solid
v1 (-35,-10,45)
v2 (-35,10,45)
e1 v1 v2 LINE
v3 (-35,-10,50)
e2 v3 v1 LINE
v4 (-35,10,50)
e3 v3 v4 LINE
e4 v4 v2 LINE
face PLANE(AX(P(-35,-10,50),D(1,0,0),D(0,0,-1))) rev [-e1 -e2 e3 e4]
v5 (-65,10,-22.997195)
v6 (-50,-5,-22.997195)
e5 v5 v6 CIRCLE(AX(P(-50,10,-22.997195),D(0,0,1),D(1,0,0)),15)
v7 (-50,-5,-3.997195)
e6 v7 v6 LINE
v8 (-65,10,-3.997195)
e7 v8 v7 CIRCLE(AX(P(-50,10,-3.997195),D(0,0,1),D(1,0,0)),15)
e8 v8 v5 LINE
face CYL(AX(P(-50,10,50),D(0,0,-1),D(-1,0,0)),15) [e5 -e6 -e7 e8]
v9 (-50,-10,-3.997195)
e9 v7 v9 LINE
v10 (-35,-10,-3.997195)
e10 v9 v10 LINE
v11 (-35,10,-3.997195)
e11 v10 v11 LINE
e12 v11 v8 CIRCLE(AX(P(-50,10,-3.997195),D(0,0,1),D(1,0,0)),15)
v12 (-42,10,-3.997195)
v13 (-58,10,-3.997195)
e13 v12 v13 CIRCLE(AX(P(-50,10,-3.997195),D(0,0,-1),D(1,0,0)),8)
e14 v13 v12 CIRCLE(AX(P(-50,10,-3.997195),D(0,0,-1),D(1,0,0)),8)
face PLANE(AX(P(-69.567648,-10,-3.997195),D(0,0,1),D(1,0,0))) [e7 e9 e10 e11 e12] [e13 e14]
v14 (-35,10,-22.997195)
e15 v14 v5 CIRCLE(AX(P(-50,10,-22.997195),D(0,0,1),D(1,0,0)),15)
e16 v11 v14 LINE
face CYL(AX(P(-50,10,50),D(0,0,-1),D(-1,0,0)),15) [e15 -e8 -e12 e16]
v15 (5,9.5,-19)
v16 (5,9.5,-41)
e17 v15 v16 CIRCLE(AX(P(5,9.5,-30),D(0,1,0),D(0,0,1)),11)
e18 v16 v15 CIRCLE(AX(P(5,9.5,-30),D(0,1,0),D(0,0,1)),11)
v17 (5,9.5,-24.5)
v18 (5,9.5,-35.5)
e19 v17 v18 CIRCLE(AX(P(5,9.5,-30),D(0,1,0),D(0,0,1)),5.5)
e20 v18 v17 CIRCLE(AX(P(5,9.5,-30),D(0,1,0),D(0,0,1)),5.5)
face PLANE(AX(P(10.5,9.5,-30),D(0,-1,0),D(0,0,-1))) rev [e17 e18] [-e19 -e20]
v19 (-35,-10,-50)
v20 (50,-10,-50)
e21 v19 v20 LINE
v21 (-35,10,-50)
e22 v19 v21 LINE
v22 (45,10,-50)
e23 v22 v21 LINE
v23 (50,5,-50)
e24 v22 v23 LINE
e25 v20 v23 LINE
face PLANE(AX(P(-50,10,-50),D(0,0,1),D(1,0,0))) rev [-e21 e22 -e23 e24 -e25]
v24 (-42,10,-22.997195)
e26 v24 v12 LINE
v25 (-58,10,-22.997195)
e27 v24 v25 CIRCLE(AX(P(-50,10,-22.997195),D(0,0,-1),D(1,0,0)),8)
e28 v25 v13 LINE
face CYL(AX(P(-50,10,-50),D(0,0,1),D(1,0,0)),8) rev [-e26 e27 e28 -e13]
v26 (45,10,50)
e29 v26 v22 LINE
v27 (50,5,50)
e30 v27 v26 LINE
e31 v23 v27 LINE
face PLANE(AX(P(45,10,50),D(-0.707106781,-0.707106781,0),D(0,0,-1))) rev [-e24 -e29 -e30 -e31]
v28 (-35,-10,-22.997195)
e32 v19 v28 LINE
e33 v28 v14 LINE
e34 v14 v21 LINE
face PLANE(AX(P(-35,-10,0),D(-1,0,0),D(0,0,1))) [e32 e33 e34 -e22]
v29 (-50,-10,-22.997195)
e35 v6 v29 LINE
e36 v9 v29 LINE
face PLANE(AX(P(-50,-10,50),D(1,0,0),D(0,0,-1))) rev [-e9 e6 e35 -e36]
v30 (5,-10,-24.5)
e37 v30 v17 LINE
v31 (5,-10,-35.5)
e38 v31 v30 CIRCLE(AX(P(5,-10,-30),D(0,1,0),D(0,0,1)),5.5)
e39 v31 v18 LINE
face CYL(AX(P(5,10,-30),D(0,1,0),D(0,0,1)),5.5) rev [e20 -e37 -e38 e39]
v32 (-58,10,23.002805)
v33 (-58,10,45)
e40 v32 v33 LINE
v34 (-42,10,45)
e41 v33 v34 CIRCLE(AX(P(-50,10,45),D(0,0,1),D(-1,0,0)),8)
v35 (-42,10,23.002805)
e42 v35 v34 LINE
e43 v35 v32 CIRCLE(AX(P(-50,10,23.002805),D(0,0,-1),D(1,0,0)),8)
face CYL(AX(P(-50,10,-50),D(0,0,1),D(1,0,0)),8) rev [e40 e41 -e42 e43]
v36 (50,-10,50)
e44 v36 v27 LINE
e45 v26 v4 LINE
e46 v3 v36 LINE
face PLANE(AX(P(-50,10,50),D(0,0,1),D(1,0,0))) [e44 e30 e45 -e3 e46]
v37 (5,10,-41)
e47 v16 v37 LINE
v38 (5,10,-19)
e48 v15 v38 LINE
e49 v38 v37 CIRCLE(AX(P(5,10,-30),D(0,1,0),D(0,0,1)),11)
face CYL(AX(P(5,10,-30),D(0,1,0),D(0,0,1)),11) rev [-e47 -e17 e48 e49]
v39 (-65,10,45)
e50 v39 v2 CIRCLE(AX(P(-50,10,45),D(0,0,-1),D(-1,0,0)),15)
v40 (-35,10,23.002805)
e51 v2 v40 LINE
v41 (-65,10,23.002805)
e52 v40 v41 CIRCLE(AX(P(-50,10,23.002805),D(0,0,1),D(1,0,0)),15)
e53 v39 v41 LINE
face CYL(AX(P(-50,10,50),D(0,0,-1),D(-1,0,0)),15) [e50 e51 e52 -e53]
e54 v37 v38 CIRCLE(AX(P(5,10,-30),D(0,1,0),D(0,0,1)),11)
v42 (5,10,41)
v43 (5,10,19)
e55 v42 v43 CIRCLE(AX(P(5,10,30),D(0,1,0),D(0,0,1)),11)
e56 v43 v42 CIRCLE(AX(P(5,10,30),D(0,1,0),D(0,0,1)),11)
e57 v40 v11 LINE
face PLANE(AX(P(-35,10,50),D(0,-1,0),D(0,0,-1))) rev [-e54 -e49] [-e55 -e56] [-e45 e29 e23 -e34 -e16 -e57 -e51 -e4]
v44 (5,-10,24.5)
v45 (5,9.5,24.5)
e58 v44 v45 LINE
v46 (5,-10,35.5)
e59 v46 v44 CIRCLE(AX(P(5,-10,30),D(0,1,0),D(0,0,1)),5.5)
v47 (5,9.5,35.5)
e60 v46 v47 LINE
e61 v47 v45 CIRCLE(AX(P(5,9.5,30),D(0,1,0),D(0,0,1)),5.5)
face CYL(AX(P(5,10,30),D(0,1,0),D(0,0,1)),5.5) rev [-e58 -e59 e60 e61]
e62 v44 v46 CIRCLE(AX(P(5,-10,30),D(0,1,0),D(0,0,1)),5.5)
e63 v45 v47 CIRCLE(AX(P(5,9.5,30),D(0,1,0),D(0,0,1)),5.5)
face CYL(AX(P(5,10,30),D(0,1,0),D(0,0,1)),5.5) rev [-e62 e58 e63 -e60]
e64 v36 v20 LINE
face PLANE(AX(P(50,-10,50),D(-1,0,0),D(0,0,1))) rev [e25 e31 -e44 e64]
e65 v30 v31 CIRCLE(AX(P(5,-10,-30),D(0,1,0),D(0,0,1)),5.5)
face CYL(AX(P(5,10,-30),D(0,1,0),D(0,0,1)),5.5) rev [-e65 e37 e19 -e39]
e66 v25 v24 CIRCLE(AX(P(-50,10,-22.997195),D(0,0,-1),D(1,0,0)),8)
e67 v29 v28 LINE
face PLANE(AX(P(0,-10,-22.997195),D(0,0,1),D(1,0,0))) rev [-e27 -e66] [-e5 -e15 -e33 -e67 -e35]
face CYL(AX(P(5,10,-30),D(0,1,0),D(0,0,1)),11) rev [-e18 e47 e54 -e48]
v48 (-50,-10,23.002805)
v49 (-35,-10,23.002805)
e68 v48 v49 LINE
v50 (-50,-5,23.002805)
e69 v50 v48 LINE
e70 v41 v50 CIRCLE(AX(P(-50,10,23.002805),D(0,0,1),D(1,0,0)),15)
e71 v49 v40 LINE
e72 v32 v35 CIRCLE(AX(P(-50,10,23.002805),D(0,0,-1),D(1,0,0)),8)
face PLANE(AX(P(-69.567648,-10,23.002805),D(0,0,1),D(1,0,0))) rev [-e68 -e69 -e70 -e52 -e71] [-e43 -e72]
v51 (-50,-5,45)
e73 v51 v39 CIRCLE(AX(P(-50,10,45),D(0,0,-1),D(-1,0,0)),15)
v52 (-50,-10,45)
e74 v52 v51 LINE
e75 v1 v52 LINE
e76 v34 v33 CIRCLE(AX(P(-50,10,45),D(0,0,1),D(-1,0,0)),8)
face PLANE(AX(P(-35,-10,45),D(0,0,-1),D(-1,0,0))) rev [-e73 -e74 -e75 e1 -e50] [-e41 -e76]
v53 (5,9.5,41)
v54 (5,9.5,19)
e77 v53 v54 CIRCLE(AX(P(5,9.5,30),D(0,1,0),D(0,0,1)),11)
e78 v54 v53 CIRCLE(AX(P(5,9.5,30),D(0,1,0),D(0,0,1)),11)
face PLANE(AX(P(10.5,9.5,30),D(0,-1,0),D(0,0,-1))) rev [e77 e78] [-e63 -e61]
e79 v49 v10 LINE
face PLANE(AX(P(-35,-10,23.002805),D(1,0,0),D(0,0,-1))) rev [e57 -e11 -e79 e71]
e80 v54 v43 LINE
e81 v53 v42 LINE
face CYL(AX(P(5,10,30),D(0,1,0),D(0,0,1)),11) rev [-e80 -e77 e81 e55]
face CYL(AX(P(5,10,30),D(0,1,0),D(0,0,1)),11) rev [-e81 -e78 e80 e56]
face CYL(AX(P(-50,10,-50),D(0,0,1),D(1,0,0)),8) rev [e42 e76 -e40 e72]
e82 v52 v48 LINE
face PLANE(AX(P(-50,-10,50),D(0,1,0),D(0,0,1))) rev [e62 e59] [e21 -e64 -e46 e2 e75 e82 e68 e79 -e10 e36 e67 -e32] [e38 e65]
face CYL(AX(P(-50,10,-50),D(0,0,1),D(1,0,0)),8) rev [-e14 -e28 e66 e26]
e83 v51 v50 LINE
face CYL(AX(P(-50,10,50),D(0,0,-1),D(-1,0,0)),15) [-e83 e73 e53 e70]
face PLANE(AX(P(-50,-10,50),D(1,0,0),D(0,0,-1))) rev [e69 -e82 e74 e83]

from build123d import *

# Parameters (mm, degrees)
EXTRUDE_2_DEPTH               = 50
CUT_EXTRUDE_1_DEPTH           = 122.86057607
CUT_EXTRUDE_1_DEPTH_BACK      = 122.86057607
SKETCH_2_R                    = 8
CUT_EXTRUDE_8_DEPTH           = 85.409715081
CUT_EXTRUDE_8_DEPTH_BACK      = 85.409715081
SKETCH_3_W                    = 34.567648094
SKETCH_3_H                    = 27
SKETCH_3_W_2                  = 34.56764798
SKETCH_3_H_2                  = 5
CHAMFER_1_SIZE                = 5
HOLE_WIZARD_M10_1_D           = 11
HOLE_WIZARD_M10_1_CBORE_D     = 22
HOLE_WIZARD_M10_1_CBORE_DEPTH = 0.5


with BuildPart() as part:
    # 草图1 → 凸台-拉伸2 (new, symmetric)
    with BuildSketch(Plane.XY):
        with BuildLine():
            Line((-50, -10), (50, -10))
            Line((50, -10), (50, 10))
            Line((50, 10), (-35, 10))
            ThreePointArc((-35, 10), (-60.606601718, 20.606601718), (-50, -5))
            Line((-50, -5), (-50, -10))
        make_face()
    extrude(amount=EXTRUDE_2_DEPTH, both=True)

    # 草图2 → 切除-拉伸1 (cut, two sides: drawn at the far end of the back side and taken through both)
    with BuildSketch(Plane.XY.offset(50).offset(-CUT_EXTRUDE_1_DEPTH_BACK)):
        with Locations((-50, 10)):
            Circle(SKETCH_2_R)
    extrude(amount=CUT_EXTRUDE_1_DEPTH + CUT_EXTRUDE_1_DEPTH_BACK, mode=Mode.SUBTRACT)

    # 草图3 → 切除-拉伸8 (cut, two sides: drawn at the far end of the back side and taken through both)
    with BuildSketch(Plane(origin=(0, 10, 0), x_dir=(1, 0, 0), z_dir=(0, 1, 0)).offset(-CUT_EXTRUDE_8_DEPTH_BACK)):
        Polygon((-69.567648094, 22.997195123), (-35, 22.997195123), (-35, 50), (-69.107419327, 50), align=None)
        with Locations((-52.283824047, -9.502804877)):
            Rectangle(SKETCH_3_W, SKETCH_3_H)
        with Locations((-52.28382399, -47.5)):
            Rectangle(SKETCH_3_W_2, SKETCH_3_H_2)
    extrude(amount=CUT_EXTRUDE_8_DEPTH + CUT_EXTRUDE_8_DEPTH_BACK, mode=Mode.SUBTRACT)

    # 倒角1
    chamfer_1_edges = [part.edges().sort_by_distance(p)[0] for p in [
        (50, 10, 0),
    ]]
    chamfer(chamfer_1_edges, length=CHAMFER_1_SIZE)

    # M10 六角头螺栓的柱形沉头孔1 (through all)
    with Locations(Plane(origin=(5, 10, -30), x_dir=(0, 0, 1), z_dir=(0, 1, 0))):
        with Locations((0, 0)):
            hole_wizard_m10_1 = CounterBoreHole(HOLE_WIZARD_M10_1_D / 2, HOLE_WIZARD_M10_1_CBORE_D / 2, HOLE_WIZARD_M10_1_CBORE_DEPTH)

    # 镜向1: M10 六角头螺栓的柱形沉头孔1 across plane
    add(hole_wizard_m10_1.mirror(Plane.XY), mode=Mode.SUBTRACT)


solid = part.part
